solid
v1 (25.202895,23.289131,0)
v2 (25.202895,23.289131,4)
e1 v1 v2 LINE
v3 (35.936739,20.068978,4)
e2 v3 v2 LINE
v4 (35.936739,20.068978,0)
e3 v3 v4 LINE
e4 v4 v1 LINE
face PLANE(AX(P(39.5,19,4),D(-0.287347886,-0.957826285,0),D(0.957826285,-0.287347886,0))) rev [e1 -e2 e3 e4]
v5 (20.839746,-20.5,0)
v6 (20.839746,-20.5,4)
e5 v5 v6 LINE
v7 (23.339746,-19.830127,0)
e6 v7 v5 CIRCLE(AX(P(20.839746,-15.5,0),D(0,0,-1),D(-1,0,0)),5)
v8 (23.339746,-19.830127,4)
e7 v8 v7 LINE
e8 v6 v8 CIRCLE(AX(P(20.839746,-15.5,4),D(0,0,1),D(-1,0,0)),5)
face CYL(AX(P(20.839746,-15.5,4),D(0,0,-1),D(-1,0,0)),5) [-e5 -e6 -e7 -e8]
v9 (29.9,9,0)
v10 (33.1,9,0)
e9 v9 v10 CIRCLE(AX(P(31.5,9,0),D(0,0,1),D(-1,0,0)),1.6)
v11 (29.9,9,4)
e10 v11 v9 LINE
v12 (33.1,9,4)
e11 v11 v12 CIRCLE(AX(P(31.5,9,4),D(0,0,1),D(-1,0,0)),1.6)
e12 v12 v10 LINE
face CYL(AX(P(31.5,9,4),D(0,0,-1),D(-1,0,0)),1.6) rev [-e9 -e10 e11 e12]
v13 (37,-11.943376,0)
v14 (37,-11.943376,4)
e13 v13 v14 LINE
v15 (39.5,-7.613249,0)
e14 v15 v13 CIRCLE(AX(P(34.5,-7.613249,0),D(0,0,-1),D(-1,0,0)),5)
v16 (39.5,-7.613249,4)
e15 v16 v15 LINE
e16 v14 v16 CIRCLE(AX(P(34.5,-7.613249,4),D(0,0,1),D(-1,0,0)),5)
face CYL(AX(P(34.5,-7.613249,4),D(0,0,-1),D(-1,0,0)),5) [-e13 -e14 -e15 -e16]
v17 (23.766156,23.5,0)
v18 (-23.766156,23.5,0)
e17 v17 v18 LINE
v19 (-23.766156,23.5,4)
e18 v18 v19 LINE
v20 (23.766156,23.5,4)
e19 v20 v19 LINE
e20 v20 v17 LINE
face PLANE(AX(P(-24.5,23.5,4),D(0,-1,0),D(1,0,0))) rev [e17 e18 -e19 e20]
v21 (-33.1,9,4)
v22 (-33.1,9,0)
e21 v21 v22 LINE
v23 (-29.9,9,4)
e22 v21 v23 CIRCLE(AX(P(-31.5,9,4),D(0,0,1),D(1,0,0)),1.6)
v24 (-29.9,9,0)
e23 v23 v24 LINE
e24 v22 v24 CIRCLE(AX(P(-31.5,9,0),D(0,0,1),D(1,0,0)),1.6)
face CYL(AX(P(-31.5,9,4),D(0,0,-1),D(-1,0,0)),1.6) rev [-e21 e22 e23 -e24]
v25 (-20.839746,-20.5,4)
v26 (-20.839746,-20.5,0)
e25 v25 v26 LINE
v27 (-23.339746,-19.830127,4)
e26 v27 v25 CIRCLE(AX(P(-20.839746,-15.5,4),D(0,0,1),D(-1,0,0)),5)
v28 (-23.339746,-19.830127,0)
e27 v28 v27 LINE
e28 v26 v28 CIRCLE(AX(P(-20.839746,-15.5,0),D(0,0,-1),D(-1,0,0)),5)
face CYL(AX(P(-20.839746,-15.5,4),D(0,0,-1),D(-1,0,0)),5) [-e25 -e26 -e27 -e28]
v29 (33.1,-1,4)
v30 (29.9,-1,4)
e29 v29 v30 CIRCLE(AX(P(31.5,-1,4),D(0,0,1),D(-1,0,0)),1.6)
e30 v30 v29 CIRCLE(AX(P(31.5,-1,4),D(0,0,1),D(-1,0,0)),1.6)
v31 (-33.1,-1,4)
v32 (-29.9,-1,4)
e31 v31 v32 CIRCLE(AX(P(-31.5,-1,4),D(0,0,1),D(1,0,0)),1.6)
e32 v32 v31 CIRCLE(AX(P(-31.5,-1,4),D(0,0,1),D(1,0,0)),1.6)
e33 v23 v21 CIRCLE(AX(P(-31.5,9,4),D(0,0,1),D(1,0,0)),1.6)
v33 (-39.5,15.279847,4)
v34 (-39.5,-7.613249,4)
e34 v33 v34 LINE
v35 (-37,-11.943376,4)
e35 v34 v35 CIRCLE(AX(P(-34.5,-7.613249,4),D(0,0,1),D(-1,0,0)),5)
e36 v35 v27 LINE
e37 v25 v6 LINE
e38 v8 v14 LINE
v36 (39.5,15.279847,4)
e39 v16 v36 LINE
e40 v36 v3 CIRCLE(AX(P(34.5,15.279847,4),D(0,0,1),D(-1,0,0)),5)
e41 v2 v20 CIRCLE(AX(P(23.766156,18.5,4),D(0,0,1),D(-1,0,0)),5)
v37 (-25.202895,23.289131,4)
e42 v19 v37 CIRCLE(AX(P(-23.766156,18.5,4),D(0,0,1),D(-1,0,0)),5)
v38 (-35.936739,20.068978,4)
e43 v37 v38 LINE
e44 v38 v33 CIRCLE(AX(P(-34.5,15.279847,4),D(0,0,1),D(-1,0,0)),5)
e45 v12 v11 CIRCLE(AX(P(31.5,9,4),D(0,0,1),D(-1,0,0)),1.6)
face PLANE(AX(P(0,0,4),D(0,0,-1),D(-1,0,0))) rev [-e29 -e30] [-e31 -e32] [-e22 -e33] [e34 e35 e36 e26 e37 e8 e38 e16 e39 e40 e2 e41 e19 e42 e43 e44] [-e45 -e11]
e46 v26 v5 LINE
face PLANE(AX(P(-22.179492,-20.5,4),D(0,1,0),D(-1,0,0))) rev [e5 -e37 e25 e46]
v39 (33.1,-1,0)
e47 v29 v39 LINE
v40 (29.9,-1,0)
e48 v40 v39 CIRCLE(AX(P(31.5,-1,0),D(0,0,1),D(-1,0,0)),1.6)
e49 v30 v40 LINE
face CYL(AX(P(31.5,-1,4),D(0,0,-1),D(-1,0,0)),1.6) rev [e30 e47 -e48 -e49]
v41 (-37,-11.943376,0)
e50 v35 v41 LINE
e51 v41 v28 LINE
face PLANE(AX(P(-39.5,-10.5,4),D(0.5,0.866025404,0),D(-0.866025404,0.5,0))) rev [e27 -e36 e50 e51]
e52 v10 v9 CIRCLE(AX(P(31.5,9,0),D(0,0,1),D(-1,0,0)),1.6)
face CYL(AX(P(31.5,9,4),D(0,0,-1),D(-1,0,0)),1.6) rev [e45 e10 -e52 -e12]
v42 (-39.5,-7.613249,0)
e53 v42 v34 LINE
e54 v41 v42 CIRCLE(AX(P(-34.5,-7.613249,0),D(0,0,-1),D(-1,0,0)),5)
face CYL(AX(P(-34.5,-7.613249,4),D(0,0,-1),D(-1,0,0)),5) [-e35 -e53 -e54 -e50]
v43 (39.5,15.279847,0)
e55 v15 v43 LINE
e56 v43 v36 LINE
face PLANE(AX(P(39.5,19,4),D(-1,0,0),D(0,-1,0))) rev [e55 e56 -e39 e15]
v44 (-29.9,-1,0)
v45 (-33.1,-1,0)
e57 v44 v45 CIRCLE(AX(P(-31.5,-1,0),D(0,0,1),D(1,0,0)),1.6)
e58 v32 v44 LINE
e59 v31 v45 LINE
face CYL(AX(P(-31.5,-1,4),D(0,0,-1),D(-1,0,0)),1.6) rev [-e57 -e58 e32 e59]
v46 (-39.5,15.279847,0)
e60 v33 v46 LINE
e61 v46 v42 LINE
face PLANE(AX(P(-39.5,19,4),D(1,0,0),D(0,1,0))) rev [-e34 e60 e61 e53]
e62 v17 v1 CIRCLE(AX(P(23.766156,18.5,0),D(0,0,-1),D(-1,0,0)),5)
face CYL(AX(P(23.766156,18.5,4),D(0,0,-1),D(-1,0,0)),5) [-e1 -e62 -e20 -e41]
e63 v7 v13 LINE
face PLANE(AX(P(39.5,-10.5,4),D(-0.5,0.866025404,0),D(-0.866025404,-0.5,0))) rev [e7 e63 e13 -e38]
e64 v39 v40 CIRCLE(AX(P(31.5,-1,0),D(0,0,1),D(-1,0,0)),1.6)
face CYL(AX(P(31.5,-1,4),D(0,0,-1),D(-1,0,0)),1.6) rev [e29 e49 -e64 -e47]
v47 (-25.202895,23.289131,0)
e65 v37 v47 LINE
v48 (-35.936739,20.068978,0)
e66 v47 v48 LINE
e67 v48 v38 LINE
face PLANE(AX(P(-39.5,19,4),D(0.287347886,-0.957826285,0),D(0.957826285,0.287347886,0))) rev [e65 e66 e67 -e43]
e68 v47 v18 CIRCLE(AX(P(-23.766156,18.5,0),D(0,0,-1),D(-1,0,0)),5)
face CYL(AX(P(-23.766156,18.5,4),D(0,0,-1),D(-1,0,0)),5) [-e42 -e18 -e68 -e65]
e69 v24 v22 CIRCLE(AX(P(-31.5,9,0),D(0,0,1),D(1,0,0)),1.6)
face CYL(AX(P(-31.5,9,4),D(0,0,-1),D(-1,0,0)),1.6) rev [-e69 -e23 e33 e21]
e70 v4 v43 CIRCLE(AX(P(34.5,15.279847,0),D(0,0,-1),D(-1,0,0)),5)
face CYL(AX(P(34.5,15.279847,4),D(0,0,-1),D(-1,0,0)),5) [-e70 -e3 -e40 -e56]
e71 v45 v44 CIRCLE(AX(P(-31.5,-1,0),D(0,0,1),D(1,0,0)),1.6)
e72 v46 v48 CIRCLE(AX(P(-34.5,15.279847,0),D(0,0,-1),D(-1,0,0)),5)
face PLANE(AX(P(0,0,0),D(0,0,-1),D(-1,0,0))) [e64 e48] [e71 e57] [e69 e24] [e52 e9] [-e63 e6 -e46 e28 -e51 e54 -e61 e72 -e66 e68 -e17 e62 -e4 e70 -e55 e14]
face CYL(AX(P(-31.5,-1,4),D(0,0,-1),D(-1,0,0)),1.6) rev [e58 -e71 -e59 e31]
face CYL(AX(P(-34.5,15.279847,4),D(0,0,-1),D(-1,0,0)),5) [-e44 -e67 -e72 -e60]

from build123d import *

# Parameters (mm, degrees)
SKETCH1_R           = 1.6
BOSS_EXTRUDE1_DEPTH = 4
R5_FILLET_1_R       = 5


with BuildPart() as part:
    # Sketch1 → Boss-Extrude1 (new body)
    with BuildSketch(Plane.XY):
        Polygon((-24.5, 23.5), (24.5, 23.5), (39.5, 19), (39.5, -10.5), (22.179491924, -20.5), (-22.179491924, -20.5), (-39.5, -10.5), (-39.5, 19), align=None)
        with Locations((-31.5, 9)):
            Circle(SKETCH1_R, mode=Mode.SUBTRACT)
        with Locations((-31.5, -1)):
            Circle(SKETCH1_R, mode=Mode.SUBTRACT)
        with Locations(Location((31.5, -1, 0), (0, 0, 180))):
            Circle(SKETCH1_R, mode=Mode.SUBTRACT)
        with Locations(Location((31.5, 9, 0), (0, 0, 180))):
            Circle(SKETCH1_R, mode=Mode.SUBTRACT)
    extrude(amount=BOSS_EXTRUDE1_DEPTH)

    # R5 Fillet 1
    r5_fillet_1_edges = [part.edges().sort_by_distance(p)[0] for p in [
        (-24.5, 23.5, 2),
        (24.5, 23.5, 2),
        (39.5, 19, 2),
        (39.5, -10.5, 2),
        (22.179491924, -20.5, 2),
        (-22.179491924, -20.5, 2),
        (-39.5, -10.5, 2),
        (-39.5, 19, 2),
    ]]
    fillet(r5_fillet_1_edges, radius=R5_FILLET_1_R)


solid = part.part
